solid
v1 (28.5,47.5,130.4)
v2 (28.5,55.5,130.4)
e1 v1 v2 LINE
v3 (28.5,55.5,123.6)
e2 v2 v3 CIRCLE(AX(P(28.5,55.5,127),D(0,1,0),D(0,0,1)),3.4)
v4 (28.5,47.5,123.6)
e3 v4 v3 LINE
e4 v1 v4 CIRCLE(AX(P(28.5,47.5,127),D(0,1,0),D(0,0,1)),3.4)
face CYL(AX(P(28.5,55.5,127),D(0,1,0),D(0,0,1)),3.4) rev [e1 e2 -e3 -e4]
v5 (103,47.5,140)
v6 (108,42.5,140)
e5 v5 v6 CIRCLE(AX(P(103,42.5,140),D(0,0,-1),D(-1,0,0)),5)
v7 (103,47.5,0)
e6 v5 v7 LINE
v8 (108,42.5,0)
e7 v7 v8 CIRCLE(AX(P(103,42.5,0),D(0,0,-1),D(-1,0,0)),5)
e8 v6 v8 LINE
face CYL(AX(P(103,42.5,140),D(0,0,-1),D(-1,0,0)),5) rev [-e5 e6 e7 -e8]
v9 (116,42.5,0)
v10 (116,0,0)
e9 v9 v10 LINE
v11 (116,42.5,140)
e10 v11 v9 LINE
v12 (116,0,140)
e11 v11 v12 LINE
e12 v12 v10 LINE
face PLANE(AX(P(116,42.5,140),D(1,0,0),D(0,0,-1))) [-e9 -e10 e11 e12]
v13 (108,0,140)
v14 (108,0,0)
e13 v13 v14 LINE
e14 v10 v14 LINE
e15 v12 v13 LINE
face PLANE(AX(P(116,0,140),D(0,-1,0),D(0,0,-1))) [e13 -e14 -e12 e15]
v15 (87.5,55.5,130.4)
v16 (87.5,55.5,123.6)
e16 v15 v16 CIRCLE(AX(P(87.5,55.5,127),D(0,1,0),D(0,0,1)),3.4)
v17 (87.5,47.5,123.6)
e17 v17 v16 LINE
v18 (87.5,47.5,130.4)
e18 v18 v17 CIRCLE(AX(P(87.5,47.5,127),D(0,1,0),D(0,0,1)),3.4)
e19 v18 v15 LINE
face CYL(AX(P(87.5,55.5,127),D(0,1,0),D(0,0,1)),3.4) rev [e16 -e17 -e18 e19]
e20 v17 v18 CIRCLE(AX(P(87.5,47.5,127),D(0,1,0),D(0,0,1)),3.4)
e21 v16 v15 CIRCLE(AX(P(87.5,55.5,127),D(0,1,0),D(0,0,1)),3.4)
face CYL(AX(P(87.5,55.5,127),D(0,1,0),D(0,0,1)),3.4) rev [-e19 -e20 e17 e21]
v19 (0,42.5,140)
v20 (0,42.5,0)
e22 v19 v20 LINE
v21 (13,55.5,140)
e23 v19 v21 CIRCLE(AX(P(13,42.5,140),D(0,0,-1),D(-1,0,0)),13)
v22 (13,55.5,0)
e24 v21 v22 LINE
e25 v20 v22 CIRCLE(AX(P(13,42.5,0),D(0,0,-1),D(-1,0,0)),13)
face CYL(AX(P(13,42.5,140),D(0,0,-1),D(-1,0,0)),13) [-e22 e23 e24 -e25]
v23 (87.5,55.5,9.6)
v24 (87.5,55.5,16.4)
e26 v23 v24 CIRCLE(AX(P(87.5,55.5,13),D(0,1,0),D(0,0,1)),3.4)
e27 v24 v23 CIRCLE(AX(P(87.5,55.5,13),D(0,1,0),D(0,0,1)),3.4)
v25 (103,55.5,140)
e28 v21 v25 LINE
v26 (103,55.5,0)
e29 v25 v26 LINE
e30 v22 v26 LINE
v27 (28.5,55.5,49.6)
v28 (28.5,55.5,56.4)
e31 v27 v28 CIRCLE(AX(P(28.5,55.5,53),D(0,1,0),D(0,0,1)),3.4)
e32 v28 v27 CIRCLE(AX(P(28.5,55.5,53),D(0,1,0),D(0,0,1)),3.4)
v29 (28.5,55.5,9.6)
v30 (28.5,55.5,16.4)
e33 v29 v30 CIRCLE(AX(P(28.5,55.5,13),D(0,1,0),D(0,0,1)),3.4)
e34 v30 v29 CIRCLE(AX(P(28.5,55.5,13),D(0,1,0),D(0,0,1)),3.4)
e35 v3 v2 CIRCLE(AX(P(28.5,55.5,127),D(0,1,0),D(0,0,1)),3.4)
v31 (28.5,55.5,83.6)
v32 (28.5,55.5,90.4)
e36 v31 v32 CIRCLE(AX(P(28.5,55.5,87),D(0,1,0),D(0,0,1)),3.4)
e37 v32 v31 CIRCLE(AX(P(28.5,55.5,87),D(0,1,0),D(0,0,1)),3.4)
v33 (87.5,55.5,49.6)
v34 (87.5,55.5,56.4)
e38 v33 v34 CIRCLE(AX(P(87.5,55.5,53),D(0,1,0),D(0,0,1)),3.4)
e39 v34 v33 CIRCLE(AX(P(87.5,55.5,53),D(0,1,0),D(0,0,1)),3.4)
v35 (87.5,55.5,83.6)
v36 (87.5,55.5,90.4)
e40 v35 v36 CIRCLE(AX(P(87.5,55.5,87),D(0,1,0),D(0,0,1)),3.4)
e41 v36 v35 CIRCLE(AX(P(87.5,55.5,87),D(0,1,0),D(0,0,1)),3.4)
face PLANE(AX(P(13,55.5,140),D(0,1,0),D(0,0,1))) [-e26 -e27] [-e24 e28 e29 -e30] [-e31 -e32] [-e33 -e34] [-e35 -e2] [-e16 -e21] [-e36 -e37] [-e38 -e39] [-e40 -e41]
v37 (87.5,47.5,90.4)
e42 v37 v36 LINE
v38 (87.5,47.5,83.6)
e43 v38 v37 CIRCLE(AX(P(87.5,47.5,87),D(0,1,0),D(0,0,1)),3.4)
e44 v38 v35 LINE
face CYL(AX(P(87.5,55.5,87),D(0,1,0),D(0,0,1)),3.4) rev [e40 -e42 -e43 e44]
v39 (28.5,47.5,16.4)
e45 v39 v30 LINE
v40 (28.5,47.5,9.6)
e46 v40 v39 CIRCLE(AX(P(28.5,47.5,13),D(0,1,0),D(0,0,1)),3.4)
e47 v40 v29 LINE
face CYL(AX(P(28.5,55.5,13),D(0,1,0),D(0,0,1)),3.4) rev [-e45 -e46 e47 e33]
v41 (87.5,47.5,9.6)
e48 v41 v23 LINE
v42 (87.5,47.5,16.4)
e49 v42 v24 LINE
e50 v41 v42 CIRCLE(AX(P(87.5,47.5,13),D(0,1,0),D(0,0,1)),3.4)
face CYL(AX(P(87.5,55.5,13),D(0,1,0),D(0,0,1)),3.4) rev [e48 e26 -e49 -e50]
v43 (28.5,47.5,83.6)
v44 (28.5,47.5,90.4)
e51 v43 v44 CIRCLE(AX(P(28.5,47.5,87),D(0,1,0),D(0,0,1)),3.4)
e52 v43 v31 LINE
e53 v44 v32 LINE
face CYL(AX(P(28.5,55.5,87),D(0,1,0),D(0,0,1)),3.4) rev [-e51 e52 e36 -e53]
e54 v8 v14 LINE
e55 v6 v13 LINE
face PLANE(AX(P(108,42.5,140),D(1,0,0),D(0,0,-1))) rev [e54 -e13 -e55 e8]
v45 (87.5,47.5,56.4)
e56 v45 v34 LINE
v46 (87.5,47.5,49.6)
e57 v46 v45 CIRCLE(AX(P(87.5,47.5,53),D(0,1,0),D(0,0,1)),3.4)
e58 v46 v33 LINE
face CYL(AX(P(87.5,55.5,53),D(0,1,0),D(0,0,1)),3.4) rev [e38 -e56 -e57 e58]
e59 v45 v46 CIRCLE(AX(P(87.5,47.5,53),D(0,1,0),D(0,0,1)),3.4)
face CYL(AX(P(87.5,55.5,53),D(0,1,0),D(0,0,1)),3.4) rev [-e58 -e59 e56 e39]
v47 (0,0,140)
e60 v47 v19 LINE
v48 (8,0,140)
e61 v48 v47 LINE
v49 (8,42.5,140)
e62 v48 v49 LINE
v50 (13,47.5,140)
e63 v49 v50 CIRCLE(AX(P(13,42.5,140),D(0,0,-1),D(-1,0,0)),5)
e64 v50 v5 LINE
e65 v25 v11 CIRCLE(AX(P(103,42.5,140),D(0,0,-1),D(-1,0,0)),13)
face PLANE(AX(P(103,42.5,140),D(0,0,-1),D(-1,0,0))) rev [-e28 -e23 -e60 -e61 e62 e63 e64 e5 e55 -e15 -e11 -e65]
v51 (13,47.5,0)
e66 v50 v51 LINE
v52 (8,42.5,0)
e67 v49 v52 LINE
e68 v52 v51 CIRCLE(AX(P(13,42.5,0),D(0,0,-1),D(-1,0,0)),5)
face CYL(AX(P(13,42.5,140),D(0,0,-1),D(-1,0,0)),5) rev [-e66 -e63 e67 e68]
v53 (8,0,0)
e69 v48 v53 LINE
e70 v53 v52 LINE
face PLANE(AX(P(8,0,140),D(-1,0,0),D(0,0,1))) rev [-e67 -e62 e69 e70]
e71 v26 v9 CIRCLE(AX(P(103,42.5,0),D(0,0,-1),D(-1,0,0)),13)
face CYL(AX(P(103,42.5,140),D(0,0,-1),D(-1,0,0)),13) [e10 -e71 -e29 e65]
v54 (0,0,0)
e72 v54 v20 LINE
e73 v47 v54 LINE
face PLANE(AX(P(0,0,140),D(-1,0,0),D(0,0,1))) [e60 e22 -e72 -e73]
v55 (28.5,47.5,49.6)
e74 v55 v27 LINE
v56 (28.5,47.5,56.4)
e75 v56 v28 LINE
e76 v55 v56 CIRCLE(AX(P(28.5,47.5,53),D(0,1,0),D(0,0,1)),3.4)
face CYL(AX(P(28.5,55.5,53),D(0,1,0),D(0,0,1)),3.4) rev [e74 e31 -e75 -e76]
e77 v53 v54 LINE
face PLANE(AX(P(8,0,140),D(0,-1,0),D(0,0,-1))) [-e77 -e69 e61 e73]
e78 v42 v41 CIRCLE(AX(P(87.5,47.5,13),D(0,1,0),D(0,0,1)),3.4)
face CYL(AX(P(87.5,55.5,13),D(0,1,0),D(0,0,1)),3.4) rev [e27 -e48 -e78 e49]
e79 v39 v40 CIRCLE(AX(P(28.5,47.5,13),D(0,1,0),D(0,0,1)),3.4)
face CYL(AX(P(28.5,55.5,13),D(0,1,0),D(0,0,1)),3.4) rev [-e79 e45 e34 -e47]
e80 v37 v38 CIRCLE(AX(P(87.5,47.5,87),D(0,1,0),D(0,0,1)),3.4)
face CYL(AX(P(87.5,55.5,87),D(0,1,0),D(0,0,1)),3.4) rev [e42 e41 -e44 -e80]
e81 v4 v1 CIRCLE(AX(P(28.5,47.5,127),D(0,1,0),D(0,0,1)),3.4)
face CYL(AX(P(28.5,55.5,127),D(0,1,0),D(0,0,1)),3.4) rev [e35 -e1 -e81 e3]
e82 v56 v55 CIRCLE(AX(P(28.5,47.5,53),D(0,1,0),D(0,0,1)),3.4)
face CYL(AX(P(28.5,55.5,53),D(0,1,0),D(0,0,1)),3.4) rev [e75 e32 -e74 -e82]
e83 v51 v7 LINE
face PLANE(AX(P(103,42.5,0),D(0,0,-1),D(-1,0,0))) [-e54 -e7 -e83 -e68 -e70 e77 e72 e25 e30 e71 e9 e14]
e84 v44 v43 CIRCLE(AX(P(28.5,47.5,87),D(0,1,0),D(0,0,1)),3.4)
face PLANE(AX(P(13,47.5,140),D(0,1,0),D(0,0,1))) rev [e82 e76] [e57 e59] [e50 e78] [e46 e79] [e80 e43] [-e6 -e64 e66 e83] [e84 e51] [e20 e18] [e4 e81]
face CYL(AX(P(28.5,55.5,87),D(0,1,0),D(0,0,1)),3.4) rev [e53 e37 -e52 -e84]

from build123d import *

# Parameters (mm, degrees)
BOSS_EXTRUDE1_DEPTH   = 140
M8_TAPPED_HOLE1_D     = 6.8
M8_TAPPED_HOLE1_DEPTH = 19.75
M8_TAPPED_HOLE1_TIP   = 2.042926105


with BuildPart() as part:
    # Sketch1 → Boss-Extrude1 (new body)
    with BuildSketch(Plane.XY):
        with BuildLine():
            Line((0, 0), (0, 42.5))
            ThreePointArc((0, 42.5), (3.807611845, 51.692388155), (13, 55.5))
            Line((13, 55.5), (103, 55.5))
            ThreePointArc((103, 55.5), (112.192388155, 51.692388155), (116, 42.5))
            Line((116, 42.5), (116, 0))
            Line((116, 0), (108, 0))
            Line((108, 0), (108, 42.5))
            ThreePointArc((108, 42.5), (106.535533906, 46.035533906), (103, 47.5))
            Line((103, 47.5), (13, 47.5))
            ThreePointArc((13, 47.5), (9.464466094, 46.035533906), (8, 42.5))
            Line((8, 42.5), (8, 0))
            Line((8, 0), (0, 0))
        make_face()
    extrude(amount=BOSS_EXTRUDE1_DEPTH)

    # M8 Tapped Hole1
    with Locations(Plane(origin=(0, 55.5, 0), x_dir=(1, 0, 0), z_dir=(0, 1, 0))):
        with Locations((28.5, -13), (87.5, -13), (87.5, -53), (28.5, -53), (28.5, -87), (87.5, -87), (87.5, -127), (28.5, -127)):
            Hole(M8_TAPPED_HOLE1_D / 2, depth=M8_TAPPED_HOLE1_DEPTH)
            with Locations((0, 0, -(M8_TAPPED_HOLE1_DEPTH + M8_TAPPED_HOLE1_TIP / 2))):  # 118° drill point
                Cone(0, M8_TAPPED_HOLE1_D / 2, M8_TAPPED_HOLE1_TIP, mode=Mode.SUBTRACT)


solid = part.part
